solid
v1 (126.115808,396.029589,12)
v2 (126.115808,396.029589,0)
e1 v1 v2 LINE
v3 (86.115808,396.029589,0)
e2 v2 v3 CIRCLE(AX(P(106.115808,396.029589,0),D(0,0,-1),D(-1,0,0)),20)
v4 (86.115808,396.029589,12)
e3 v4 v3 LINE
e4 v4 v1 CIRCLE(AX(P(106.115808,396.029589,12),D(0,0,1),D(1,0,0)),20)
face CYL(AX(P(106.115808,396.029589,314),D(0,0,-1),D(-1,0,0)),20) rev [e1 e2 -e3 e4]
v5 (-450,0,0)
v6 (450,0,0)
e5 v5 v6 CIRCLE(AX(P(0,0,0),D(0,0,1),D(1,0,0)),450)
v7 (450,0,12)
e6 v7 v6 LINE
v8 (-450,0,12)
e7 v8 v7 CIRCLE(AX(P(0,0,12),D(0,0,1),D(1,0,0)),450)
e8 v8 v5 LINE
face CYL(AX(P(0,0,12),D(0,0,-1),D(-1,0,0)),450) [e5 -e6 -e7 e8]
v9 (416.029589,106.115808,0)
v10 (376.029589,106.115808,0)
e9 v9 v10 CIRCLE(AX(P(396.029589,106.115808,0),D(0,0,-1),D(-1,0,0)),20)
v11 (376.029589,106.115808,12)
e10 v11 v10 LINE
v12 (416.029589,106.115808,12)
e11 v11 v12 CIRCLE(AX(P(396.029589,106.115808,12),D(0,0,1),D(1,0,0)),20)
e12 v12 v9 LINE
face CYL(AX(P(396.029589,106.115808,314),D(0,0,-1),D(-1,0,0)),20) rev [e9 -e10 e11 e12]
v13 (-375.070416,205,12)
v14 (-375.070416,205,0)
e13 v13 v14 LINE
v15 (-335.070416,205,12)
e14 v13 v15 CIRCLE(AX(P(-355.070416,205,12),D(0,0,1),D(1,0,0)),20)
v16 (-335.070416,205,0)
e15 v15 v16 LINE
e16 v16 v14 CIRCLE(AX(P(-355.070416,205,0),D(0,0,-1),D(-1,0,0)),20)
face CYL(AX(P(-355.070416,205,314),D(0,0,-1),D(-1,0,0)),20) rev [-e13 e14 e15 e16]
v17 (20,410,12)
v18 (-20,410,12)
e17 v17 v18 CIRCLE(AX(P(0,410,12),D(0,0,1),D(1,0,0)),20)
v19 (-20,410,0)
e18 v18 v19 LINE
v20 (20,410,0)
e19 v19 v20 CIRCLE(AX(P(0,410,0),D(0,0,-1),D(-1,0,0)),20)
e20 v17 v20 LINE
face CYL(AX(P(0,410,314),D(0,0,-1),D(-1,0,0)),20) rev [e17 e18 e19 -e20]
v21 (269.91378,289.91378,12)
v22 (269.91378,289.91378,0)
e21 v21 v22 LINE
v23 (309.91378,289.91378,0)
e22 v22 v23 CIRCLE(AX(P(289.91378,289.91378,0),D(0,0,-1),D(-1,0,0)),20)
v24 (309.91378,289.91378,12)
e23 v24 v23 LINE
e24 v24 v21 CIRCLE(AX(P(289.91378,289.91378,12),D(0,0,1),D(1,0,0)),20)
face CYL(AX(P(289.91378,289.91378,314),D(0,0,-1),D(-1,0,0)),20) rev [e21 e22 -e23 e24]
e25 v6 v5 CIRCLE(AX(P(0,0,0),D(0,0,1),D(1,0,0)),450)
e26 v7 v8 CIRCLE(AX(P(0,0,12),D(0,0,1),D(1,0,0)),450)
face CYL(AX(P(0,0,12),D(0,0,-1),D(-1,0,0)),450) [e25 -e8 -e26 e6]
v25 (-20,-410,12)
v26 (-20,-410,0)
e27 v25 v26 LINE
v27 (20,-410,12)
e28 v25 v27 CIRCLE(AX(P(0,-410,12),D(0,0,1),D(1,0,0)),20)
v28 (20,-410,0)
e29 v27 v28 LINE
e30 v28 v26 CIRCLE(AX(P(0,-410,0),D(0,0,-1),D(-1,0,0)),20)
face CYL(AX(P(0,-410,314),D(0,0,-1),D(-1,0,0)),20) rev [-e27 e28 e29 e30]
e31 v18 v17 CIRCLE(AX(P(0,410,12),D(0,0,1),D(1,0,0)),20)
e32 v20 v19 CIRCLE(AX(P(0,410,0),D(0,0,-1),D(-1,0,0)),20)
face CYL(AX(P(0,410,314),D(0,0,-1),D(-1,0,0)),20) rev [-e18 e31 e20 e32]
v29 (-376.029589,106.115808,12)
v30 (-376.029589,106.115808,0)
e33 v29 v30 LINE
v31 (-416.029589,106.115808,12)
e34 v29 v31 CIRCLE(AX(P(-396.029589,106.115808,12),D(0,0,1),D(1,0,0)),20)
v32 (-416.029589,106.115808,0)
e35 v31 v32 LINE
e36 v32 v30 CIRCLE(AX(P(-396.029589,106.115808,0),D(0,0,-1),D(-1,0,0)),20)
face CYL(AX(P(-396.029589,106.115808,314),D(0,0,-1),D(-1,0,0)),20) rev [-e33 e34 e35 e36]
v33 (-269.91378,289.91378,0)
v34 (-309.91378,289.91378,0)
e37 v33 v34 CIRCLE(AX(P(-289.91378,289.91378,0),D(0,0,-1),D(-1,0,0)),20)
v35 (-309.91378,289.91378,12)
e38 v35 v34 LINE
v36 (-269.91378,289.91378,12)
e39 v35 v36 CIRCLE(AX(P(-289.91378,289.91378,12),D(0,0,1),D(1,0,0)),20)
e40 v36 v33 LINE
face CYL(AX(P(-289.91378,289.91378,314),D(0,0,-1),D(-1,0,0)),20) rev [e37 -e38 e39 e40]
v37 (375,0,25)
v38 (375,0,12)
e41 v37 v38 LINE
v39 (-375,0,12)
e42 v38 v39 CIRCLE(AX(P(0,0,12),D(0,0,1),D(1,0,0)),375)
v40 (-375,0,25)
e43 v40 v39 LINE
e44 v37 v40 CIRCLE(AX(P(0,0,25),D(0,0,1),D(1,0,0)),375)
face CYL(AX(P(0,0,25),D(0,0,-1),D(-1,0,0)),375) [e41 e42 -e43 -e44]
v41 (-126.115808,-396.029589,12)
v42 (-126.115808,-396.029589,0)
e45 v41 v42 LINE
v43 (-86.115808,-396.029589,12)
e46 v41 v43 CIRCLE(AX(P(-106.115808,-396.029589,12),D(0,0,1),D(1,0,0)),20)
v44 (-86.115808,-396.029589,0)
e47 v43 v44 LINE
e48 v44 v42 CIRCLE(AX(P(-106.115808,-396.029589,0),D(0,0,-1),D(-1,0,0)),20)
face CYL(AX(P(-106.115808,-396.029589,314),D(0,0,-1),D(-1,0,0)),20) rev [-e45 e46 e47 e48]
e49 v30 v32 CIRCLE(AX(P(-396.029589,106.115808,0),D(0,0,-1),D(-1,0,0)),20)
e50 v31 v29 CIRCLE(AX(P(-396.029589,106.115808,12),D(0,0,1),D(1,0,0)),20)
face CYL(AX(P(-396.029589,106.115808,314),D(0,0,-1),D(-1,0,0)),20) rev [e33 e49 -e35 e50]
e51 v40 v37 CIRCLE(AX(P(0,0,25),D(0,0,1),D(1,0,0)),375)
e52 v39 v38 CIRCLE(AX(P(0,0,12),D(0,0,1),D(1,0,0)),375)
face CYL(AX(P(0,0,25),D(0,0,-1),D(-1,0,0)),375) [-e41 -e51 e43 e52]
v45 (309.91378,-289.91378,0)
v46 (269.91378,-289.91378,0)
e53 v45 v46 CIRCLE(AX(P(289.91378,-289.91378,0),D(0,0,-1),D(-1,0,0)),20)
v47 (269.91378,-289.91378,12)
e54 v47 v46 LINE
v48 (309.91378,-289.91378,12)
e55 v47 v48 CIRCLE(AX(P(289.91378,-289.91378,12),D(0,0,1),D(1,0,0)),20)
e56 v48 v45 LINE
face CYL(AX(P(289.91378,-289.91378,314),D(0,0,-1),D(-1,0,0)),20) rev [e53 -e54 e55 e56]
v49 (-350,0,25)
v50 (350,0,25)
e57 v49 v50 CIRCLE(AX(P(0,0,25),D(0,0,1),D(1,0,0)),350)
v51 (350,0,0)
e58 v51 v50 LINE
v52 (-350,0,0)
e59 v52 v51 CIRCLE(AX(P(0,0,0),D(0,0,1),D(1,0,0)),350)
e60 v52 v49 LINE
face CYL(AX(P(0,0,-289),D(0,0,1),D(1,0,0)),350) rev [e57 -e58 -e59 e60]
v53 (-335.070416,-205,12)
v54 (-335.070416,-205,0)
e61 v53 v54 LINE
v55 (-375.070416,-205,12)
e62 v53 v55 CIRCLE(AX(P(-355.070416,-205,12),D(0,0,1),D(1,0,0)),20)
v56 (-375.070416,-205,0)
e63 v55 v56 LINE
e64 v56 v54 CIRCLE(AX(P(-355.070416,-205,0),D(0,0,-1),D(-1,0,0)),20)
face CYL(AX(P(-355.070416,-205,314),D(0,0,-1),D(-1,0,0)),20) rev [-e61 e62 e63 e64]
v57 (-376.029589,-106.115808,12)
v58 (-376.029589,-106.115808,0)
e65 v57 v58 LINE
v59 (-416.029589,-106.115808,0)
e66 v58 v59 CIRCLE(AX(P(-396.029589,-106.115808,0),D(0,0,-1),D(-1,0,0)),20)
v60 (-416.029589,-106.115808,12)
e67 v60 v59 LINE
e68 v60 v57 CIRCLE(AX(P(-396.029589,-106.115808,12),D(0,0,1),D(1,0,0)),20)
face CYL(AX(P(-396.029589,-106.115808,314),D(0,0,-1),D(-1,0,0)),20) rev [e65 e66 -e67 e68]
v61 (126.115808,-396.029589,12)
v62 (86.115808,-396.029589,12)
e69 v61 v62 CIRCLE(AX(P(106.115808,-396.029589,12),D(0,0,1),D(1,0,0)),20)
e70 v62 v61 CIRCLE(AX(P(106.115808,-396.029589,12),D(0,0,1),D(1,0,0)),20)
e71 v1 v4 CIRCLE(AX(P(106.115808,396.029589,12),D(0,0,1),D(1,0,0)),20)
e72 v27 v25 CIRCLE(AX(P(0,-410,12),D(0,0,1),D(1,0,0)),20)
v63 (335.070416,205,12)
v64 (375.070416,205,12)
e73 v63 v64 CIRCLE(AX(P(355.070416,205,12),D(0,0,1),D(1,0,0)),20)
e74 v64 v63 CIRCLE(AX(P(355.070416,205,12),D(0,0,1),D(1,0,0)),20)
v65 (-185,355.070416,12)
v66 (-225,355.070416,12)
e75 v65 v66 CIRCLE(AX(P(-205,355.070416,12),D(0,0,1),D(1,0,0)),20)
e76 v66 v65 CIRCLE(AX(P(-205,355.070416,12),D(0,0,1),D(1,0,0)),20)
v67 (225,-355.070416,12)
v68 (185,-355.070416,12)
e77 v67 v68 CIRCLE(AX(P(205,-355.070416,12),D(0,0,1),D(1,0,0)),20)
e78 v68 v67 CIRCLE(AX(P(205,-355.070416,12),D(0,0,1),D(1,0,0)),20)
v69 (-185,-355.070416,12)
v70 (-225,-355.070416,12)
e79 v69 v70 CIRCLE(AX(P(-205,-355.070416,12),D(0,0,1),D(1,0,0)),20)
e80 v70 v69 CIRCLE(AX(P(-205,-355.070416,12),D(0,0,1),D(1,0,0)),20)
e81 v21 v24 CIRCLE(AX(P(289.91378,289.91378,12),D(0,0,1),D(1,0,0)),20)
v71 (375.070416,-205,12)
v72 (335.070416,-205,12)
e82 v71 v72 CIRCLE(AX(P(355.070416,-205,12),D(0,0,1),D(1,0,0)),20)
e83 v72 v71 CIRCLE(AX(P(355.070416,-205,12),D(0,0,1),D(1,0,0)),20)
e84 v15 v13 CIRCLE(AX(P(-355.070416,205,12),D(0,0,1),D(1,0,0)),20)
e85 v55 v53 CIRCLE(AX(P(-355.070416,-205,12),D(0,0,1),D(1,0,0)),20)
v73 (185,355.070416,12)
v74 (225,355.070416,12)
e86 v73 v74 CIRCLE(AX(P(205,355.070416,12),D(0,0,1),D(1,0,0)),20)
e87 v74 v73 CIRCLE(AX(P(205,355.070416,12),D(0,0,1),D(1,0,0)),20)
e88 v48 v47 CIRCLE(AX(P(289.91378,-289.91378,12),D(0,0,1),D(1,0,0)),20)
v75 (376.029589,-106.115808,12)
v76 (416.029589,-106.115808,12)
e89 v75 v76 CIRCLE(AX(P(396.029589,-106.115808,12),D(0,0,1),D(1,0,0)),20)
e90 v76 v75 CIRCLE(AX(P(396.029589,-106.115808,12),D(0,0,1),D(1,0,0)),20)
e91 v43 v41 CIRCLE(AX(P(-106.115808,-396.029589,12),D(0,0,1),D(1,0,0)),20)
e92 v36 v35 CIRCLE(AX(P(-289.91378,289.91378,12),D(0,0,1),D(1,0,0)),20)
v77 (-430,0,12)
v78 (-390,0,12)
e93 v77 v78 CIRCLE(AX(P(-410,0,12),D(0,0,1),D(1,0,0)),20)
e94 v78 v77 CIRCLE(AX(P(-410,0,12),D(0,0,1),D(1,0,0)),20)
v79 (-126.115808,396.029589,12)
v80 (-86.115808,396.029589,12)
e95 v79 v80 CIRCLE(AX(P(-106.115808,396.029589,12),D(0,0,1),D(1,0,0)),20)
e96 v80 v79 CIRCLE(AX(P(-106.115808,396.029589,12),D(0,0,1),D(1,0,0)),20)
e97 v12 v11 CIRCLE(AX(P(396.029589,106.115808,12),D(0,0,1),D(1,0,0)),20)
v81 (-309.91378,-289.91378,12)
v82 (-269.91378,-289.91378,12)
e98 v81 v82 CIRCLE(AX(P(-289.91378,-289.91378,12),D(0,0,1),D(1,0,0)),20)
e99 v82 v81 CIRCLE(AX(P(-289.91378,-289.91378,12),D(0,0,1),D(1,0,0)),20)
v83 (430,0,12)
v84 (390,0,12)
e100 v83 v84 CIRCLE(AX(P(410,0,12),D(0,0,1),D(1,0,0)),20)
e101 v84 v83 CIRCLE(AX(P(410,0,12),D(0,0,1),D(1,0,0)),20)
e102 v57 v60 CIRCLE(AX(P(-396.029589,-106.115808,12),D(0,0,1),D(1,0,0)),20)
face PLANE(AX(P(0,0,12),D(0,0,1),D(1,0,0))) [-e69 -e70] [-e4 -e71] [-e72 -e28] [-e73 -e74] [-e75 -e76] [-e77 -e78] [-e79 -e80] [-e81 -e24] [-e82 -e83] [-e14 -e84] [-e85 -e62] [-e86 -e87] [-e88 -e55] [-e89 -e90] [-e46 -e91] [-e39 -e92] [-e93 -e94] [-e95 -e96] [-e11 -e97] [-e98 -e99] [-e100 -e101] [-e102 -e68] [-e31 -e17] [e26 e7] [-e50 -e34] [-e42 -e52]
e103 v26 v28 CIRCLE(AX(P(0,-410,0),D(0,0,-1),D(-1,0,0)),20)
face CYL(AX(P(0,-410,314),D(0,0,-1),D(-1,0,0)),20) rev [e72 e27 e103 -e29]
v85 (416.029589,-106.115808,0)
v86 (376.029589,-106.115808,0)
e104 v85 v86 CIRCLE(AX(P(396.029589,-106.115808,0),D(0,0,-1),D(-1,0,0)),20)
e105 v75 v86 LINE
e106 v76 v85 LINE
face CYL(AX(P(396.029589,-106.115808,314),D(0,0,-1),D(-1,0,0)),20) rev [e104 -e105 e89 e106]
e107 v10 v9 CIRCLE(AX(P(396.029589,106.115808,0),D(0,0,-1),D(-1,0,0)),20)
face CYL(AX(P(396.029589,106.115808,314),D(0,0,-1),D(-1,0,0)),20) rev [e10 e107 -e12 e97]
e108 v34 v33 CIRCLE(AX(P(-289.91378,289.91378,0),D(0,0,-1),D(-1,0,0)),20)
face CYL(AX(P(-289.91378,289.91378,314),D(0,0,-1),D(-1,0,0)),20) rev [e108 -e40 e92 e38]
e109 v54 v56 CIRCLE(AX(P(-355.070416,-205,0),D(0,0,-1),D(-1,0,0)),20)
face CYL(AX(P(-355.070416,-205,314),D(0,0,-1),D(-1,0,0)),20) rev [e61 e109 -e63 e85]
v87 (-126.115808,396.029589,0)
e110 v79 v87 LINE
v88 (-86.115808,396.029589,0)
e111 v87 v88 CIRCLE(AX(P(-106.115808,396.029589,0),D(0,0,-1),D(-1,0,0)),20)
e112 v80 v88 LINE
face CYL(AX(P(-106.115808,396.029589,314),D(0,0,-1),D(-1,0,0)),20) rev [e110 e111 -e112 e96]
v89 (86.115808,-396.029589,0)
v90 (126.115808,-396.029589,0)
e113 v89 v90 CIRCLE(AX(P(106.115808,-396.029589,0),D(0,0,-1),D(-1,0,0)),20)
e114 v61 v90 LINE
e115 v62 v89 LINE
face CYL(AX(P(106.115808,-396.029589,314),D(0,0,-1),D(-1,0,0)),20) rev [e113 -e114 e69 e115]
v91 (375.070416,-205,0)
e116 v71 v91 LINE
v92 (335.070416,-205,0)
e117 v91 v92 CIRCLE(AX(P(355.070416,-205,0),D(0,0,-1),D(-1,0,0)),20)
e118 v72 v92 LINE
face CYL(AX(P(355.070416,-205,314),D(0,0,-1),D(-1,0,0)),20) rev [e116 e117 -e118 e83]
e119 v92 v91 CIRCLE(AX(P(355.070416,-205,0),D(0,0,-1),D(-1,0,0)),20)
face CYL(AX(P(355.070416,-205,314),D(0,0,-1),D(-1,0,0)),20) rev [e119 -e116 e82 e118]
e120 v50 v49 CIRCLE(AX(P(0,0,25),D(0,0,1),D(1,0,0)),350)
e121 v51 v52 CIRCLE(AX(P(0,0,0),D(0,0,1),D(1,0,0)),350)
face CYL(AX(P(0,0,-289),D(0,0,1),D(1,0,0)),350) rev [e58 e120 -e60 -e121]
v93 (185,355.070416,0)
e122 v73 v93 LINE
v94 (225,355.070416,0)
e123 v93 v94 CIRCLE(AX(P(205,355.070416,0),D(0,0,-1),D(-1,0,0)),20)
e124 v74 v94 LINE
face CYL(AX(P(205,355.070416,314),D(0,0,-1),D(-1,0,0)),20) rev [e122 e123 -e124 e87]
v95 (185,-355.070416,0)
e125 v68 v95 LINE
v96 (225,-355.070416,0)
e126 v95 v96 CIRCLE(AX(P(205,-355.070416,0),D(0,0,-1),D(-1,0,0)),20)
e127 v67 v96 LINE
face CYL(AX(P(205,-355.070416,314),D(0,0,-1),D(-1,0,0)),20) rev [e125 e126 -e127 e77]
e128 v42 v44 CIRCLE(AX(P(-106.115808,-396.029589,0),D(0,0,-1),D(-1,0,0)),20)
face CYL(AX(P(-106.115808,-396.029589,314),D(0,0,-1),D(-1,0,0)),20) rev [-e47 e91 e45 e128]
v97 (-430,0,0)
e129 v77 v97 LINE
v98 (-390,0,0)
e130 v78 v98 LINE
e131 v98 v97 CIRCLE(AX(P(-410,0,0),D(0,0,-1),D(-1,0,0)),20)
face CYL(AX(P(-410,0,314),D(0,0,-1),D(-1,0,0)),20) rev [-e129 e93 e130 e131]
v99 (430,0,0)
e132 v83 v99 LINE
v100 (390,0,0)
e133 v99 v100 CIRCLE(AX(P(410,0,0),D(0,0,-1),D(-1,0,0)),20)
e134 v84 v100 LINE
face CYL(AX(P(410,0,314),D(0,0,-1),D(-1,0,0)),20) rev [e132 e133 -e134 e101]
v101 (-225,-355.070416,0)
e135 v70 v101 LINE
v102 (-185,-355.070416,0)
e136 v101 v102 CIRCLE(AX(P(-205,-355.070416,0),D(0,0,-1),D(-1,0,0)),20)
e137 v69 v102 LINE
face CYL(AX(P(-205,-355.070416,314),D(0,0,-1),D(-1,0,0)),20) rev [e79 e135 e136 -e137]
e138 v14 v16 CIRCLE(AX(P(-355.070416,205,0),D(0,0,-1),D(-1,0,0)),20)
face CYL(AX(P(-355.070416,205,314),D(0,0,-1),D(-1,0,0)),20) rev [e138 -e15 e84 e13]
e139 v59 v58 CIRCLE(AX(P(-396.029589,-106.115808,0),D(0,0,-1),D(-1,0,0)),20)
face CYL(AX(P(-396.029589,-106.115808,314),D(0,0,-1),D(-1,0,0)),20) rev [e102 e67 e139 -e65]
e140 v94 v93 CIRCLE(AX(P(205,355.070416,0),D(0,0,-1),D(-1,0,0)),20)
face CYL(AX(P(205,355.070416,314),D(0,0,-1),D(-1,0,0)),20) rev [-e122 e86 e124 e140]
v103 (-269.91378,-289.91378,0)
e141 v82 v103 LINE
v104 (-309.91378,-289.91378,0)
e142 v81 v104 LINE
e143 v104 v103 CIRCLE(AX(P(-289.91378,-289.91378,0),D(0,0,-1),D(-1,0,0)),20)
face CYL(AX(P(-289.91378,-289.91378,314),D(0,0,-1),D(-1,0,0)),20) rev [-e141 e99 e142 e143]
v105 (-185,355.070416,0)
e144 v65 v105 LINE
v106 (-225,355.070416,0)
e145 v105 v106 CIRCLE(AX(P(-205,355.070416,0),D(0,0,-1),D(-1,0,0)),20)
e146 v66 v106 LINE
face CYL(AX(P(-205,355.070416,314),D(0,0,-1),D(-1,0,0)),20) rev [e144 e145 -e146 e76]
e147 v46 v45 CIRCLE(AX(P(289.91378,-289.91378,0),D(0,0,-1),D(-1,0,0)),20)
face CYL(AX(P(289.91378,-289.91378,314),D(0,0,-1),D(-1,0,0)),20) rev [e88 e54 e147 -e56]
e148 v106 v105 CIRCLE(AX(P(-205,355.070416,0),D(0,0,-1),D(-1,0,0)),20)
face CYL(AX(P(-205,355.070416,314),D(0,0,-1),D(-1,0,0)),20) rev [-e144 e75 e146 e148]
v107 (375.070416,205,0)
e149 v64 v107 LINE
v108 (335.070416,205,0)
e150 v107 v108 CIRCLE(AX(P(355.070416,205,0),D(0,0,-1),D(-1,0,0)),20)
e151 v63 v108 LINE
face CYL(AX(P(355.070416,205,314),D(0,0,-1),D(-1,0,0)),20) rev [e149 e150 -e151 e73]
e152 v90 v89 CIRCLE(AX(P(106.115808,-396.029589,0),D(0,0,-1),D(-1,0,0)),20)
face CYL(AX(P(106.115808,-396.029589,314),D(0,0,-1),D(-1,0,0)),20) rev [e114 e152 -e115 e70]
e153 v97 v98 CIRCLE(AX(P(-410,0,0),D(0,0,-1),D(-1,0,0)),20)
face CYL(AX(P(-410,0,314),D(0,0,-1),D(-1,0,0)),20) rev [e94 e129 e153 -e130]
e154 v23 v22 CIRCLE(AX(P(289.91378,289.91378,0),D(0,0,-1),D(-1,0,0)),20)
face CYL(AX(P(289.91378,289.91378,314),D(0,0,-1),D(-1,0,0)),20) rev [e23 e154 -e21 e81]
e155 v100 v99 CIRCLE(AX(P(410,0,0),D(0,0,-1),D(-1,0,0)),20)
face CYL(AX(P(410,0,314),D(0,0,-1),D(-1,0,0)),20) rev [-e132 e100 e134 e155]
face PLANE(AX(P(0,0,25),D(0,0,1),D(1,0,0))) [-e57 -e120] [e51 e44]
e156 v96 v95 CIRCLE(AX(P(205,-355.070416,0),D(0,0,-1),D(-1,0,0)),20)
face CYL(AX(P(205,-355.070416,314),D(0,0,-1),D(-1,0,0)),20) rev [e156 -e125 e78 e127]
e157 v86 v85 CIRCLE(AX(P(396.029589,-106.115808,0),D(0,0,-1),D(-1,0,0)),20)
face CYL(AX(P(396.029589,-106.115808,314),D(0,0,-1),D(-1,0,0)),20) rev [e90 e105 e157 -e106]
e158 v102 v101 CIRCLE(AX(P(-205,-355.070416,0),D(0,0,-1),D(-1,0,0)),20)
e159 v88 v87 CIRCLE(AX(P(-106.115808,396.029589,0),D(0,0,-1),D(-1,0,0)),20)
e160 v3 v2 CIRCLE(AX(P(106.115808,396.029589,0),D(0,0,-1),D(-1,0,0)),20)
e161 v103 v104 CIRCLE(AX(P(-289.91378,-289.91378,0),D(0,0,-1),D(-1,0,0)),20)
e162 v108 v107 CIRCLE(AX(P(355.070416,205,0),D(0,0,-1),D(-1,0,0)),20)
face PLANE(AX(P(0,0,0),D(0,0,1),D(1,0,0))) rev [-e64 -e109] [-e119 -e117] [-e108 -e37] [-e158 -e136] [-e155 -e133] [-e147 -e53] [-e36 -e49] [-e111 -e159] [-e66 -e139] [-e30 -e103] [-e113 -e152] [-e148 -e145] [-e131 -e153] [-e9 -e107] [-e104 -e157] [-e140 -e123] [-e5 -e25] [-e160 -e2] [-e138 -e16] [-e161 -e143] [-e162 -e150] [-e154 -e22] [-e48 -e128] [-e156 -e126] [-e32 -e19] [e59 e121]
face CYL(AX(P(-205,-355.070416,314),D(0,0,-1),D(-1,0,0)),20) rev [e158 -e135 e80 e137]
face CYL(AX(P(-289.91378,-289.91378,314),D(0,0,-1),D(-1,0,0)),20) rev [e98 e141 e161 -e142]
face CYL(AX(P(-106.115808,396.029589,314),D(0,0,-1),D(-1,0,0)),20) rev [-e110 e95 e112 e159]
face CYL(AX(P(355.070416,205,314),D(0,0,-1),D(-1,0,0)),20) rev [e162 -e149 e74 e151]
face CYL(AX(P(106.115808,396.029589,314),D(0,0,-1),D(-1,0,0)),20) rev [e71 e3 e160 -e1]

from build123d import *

# Parameters (mm, degrees)
SKETCH_1_R          = 450
EXTRUDE_1_DEPTH     = 12
SKETCH_2_R          = 375
EXTRUDE_2_DEPTH     = 13
SKETCH_3_R          = 20
CUT_EXTRUDE_2_DEPTH = 314
SKETCH_4_R          = 350
CUT_EXTRUDE_3_DEPTH = 314


with BuildPart() as part:
    # 草图1 → 凸台-拉伸1 (new body)
    with BuildSketch(Plane.XY):
        Circle(SKETCH_1_R)
    extrude(amount=EXTRUDE_1_DEPTH)

    # 草图2 → 凸台-拉伸2 (add)
    with BuildSketch(Plane.XY.offset(12)):
        with Locations(Location((0, 0, 0), (0, 0, 180))):
            Circle(SKETCH_2_R)
    extrude(amount=EXTRUDE_2_DEPTH)

    # 草图3 → 切除-拉伸2 (cut)
    with BuildSketch(Plane(origin=(0, 0, 0), x_dir=(-1, 0, 0), z_dir=(0, 0, -1))):
        with Locations((0, 410)):
            Circle(SKETCH_3_R)
        with Locations((106.115808492, 396.029588779)):
            Circle(SKETCH_3_R)
        with Locations((205, 355.070415552)):
            Circle(SKETCH_3_R)
        with Locations((289.913780286, 289.913780286)):
            Circle(SKETCH_3_R)
        with Locations((355.070415552, 205)):
            Circle(SKETCH_3_R)
        with Locations((396.029588779, 106.115808492)):
            Circle(SKETCH_3_R)
        with Locations((410, 0)):
            Circle(SKETCH_3_R)
        with Locations((396.029588779, -106.115808492)):
            Circle(SKETCH_3_R)
        with Locations((355.070415552, -205)):
            Circle(SKETCH_3_R)
        with Locations((289.913780286, -289.913780286)):
            Circle(SKETCH_3_R)
        with Locations((205, -355.070415552)):
            Circle(SKETCH_3_R)
        with Locations((106.115808492, -396.029588779)):
            Circle(SKETCH_3_R)
        with Locations((0, -410)):
            Circle(SKETCH_3_R)
        with Locations((-106.115808492, -396.029588779)):
            Circle(SKETCH_3_R)
        with Locations((-205, -355.070415552)):
            Circle(SKETCH_3_R)
        with Locations((-289.913780286, -289.913780286)):
            Circle(SKETCH_3_R)
        with Locations((-355.070415552, -205)):
            Circle(SKETCH_3_R)
        with Locations((-396.029588779, -106.115808492)):
            Circle(SKETCH_3_R)
        with Locations((-410, 0)):
            Circle(SKETCH_3_R)
        with Locations((-396.029588779, 106.115808492)):
            Circle(SKETCH_3_R)
        with Locations((-355.070415552, 205)):
            Circle(SKETCH_3_R)
        with Locations((-289.913780286, 289.913780286)):
            Circle(SKETCH_3_R)
        with Locations((-205, 355.070415552)):
            Circle(SKETCH_3_R)
        with Locations((-106.115808492, 396.029588779)):
            Circle(SKETCH_3_R)
    extrude(amount=-CUT_EXTRUDE_2_DEPTH, mode=Mode.SUBTRACT)

    # 草图4 → 切除-拉伸3 (cut)
    with BuildSketch(Plane.XY.offset(25)):
        Circle(SKETCH_4_R)
    extrude(amount=-CUT_EXTRUDE_3_DEPTH, mode=Mode.SUBTRACT)


solid = part.part
